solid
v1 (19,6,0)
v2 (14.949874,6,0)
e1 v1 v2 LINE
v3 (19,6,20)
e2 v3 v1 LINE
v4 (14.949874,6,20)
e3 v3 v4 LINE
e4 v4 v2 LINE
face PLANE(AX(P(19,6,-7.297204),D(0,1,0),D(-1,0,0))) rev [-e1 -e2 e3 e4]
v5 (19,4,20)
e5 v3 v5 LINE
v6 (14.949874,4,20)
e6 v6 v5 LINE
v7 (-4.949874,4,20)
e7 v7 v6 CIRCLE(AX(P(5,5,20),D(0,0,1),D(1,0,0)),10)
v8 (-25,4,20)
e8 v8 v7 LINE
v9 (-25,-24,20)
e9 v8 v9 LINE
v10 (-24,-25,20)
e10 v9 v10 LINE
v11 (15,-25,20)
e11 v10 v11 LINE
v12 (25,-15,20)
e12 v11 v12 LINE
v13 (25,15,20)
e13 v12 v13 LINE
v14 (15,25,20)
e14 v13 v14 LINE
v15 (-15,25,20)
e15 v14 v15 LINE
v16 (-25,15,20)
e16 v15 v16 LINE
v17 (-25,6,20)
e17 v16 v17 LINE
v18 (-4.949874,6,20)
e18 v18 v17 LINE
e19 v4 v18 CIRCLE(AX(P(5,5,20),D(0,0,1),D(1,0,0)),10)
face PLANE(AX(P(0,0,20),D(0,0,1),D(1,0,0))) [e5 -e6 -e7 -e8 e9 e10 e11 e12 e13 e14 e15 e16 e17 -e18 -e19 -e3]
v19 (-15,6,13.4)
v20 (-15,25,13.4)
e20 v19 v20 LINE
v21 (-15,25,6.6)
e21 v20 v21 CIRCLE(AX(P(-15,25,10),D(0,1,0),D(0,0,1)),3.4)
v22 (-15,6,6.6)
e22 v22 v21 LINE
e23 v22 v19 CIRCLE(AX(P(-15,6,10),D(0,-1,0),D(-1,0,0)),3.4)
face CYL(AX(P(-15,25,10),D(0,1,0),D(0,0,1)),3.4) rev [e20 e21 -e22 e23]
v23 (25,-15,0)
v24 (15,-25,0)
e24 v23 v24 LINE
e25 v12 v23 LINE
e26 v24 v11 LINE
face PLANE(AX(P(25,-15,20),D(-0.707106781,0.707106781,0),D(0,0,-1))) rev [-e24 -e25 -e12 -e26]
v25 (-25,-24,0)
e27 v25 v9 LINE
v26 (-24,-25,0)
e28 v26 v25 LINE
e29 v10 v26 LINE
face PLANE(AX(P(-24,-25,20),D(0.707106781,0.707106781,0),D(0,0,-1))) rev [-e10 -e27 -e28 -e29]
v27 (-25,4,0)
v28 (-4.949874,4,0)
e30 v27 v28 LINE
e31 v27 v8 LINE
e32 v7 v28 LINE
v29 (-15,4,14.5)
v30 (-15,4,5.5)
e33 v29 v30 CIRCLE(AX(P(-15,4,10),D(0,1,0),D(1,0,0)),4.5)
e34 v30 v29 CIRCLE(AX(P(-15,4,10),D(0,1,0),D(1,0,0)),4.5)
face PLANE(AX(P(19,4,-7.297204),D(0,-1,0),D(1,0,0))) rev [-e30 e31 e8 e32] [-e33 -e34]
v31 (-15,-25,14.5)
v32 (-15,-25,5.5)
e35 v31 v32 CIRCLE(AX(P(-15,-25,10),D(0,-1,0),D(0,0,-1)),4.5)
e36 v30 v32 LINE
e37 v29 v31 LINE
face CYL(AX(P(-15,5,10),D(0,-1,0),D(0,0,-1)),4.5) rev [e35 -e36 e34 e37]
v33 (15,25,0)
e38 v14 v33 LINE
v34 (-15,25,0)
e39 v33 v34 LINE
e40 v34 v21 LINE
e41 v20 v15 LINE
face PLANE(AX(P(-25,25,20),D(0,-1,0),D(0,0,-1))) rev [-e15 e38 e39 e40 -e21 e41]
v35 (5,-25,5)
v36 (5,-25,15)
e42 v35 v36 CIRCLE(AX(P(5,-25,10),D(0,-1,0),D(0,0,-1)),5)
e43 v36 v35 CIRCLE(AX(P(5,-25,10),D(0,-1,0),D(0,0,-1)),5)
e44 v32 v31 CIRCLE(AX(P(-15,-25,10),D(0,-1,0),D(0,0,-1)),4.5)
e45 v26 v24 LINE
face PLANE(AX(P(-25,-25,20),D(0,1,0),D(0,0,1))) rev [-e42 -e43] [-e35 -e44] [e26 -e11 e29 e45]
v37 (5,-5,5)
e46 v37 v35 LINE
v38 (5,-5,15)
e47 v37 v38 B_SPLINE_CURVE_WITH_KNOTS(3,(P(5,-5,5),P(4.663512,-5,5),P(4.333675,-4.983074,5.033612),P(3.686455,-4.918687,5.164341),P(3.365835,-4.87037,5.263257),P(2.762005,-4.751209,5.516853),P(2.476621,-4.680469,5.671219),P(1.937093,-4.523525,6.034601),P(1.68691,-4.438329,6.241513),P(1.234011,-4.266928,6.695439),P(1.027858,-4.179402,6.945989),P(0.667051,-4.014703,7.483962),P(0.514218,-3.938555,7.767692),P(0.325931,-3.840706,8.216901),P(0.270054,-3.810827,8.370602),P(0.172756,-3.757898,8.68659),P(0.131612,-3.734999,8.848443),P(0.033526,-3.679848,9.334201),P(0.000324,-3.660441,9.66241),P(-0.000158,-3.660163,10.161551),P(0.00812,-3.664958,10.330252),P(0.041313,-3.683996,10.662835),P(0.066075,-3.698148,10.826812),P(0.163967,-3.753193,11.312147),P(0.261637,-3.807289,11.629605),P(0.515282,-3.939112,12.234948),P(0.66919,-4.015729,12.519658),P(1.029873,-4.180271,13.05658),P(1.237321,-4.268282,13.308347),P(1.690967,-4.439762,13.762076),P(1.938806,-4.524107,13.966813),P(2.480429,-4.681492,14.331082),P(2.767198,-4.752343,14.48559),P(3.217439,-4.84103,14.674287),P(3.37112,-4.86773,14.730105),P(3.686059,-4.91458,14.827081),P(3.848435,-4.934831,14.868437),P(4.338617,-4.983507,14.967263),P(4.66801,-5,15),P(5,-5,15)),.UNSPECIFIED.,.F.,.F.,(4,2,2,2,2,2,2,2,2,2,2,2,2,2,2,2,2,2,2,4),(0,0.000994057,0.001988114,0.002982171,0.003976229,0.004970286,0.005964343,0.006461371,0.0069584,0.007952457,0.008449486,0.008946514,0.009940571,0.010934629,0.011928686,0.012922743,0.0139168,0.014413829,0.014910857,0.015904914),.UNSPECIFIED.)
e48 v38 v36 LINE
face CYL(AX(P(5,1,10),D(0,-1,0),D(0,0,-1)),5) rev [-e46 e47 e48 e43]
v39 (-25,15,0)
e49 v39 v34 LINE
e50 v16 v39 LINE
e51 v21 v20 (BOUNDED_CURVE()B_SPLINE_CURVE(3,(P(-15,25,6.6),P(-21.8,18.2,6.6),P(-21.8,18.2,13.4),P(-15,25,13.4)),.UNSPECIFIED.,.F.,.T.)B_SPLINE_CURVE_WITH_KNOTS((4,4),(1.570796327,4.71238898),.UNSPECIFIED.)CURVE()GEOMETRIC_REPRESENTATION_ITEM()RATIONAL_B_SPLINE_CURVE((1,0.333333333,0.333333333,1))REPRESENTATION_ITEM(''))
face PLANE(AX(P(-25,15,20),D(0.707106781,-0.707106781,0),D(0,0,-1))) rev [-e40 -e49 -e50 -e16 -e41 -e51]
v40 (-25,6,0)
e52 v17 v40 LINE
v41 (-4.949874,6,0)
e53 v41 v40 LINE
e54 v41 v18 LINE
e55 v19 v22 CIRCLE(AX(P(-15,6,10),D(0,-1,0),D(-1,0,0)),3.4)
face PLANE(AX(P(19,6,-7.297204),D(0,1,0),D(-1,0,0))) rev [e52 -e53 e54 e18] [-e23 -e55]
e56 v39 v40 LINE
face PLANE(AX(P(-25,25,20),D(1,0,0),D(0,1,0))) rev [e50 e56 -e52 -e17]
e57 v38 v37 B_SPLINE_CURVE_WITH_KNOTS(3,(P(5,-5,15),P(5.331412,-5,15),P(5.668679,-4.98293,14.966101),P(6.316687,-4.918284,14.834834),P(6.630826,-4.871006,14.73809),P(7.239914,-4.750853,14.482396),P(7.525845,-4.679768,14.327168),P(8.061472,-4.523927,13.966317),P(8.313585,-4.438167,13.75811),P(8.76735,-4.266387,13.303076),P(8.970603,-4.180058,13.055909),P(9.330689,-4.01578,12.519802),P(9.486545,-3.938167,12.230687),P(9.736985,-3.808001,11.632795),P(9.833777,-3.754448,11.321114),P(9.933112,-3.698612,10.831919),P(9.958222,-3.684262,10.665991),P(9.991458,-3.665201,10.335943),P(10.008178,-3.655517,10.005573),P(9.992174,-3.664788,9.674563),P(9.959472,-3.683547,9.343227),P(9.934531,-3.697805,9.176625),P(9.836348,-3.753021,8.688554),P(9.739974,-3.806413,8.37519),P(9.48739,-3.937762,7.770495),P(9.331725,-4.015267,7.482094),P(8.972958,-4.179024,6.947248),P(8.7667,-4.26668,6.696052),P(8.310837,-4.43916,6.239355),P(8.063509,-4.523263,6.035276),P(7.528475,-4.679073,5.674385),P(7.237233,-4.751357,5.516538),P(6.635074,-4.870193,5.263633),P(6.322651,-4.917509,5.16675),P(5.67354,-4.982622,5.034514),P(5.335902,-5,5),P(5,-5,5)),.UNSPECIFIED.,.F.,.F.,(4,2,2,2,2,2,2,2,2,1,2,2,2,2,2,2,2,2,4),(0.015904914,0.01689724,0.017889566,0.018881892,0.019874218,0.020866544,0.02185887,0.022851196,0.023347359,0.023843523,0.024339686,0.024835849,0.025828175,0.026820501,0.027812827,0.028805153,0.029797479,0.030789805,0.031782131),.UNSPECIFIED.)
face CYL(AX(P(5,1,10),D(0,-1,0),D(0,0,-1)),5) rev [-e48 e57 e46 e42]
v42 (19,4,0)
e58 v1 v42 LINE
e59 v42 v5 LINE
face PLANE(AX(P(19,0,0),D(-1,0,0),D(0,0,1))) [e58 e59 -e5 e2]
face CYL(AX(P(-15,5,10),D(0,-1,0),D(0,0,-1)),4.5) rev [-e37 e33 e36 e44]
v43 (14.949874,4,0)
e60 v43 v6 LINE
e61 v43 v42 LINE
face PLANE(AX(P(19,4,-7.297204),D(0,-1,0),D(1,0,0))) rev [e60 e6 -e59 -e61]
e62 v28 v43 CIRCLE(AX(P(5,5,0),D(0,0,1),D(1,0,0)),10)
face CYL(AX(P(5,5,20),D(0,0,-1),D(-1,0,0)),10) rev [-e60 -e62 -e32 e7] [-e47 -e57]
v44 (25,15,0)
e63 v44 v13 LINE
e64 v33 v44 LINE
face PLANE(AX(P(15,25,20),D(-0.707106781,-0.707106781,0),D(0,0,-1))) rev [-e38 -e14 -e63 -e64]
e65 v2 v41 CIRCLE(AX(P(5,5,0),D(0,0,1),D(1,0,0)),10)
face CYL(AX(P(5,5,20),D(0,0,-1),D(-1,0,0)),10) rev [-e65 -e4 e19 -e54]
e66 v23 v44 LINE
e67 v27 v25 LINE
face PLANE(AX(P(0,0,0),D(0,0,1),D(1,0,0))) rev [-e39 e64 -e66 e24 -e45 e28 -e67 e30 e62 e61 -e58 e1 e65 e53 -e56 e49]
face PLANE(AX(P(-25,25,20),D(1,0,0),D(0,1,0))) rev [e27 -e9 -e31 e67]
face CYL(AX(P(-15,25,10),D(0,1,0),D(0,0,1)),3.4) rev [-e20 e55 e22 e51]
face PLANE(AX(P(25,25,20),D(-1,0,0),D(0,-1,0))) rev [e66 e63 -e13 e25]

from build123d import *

# Parameters (mm, degrees)
SKETCH_1_W          = 50
SKETCH_1_H          = 50
SKETCH_1_R          = 10
EXTRUDE_1_DEPTH     = 20
CHAMFER_1_SIZE      = 10
CHAMFER_2_SIZE      = 1
HOLE_WIZARD_M8_1_D  = 6.8
SKETCH_5_R          = 4.5
CUT_EXTRUDE_1_DEPTH = 30
SKETCH_6_W          = 34.59440866
SKETCH_6_H          = 2
CUT_EXTRUDE_2_DEPTH = 44
SKETCH_7_R          = 5
CUT_EXTRUDE_5_DEPTH = 26


with BuildPart() as part:
    # 草图1 → 凸台-拉伸1 (new body)
    with BuildSketch(Plane.XY):
        Rectangle(SKETCH_1_W, SKETCH_1_H)
        with Locations((5, 5)):
            Circle(SKETCH_1_R, mode=Mode.SUBTRACT)
    extrude(amount=EXTRUDE_1_DEPTH)

    # 倒角1
    chamfer_1_edges = [part.edges().sort_by_distance(p)[0] for p in [
        (25, -25, 10),
        (-25, 25, 10),
        (25, 25, 10),
    ]]
    chamfer(chamfer_1_edges, length=CHAMFER_1_SIZE)

    # 倒角2
    chamfer_2_edges = [part.edges().sort_by_distance(p)[0] for p in [
        (-25, -25, 10),
    ]]
    chamfer(chamfer_2_edges, length=CHAMFER_2_SIZE)

    # M8 螺纹孔1 (through all)
    with Locations(Plane(origin=(0, 25, 0), x_dir=(1, 0, 0), z_dir=(0, 1, 0))):
        with Locations((-15, -10)):
            Hole(HOLE_WIZARD_M8_1_D / 2)

    # 草图5 → 切除-拉伸1 (cut)
    with BuildSketch(Plane.XZ.offset(25)):
        with Locations(Location((-15, 10, 0), (0, 0, 270))):
            Circle(SKETCH_5_R)
    extrude(amount=-CUT_EXTRUDE_1_DEPTH, mode=Mode.SUBTRACT)

    # 草图6 → 切除-拉伸2 (cut)
    with BuildSketch(Plane.ZY.offset(25)):
        with Locations((10, 5)):
            Rectangle(SKETCH_6_W, SKETCH_6_H)
    extrude(amount=-CUT_EXTRUDE_2_DEPTH, mode=Mode.SUBTRACT)

    # 草图7 → 切除-拉伸5 (cut)
    with BuildSketch(Plane.XZ.offset(25)):
        with Locations(Location((5, 10, 0), (0, 0, 270))):
            Circle(SKETCH_7_R)
    extrude(amount=-CUT_EXTRUDE_5_DEPTH, mode=Mode.SUBTRACT)


solid = part.part
